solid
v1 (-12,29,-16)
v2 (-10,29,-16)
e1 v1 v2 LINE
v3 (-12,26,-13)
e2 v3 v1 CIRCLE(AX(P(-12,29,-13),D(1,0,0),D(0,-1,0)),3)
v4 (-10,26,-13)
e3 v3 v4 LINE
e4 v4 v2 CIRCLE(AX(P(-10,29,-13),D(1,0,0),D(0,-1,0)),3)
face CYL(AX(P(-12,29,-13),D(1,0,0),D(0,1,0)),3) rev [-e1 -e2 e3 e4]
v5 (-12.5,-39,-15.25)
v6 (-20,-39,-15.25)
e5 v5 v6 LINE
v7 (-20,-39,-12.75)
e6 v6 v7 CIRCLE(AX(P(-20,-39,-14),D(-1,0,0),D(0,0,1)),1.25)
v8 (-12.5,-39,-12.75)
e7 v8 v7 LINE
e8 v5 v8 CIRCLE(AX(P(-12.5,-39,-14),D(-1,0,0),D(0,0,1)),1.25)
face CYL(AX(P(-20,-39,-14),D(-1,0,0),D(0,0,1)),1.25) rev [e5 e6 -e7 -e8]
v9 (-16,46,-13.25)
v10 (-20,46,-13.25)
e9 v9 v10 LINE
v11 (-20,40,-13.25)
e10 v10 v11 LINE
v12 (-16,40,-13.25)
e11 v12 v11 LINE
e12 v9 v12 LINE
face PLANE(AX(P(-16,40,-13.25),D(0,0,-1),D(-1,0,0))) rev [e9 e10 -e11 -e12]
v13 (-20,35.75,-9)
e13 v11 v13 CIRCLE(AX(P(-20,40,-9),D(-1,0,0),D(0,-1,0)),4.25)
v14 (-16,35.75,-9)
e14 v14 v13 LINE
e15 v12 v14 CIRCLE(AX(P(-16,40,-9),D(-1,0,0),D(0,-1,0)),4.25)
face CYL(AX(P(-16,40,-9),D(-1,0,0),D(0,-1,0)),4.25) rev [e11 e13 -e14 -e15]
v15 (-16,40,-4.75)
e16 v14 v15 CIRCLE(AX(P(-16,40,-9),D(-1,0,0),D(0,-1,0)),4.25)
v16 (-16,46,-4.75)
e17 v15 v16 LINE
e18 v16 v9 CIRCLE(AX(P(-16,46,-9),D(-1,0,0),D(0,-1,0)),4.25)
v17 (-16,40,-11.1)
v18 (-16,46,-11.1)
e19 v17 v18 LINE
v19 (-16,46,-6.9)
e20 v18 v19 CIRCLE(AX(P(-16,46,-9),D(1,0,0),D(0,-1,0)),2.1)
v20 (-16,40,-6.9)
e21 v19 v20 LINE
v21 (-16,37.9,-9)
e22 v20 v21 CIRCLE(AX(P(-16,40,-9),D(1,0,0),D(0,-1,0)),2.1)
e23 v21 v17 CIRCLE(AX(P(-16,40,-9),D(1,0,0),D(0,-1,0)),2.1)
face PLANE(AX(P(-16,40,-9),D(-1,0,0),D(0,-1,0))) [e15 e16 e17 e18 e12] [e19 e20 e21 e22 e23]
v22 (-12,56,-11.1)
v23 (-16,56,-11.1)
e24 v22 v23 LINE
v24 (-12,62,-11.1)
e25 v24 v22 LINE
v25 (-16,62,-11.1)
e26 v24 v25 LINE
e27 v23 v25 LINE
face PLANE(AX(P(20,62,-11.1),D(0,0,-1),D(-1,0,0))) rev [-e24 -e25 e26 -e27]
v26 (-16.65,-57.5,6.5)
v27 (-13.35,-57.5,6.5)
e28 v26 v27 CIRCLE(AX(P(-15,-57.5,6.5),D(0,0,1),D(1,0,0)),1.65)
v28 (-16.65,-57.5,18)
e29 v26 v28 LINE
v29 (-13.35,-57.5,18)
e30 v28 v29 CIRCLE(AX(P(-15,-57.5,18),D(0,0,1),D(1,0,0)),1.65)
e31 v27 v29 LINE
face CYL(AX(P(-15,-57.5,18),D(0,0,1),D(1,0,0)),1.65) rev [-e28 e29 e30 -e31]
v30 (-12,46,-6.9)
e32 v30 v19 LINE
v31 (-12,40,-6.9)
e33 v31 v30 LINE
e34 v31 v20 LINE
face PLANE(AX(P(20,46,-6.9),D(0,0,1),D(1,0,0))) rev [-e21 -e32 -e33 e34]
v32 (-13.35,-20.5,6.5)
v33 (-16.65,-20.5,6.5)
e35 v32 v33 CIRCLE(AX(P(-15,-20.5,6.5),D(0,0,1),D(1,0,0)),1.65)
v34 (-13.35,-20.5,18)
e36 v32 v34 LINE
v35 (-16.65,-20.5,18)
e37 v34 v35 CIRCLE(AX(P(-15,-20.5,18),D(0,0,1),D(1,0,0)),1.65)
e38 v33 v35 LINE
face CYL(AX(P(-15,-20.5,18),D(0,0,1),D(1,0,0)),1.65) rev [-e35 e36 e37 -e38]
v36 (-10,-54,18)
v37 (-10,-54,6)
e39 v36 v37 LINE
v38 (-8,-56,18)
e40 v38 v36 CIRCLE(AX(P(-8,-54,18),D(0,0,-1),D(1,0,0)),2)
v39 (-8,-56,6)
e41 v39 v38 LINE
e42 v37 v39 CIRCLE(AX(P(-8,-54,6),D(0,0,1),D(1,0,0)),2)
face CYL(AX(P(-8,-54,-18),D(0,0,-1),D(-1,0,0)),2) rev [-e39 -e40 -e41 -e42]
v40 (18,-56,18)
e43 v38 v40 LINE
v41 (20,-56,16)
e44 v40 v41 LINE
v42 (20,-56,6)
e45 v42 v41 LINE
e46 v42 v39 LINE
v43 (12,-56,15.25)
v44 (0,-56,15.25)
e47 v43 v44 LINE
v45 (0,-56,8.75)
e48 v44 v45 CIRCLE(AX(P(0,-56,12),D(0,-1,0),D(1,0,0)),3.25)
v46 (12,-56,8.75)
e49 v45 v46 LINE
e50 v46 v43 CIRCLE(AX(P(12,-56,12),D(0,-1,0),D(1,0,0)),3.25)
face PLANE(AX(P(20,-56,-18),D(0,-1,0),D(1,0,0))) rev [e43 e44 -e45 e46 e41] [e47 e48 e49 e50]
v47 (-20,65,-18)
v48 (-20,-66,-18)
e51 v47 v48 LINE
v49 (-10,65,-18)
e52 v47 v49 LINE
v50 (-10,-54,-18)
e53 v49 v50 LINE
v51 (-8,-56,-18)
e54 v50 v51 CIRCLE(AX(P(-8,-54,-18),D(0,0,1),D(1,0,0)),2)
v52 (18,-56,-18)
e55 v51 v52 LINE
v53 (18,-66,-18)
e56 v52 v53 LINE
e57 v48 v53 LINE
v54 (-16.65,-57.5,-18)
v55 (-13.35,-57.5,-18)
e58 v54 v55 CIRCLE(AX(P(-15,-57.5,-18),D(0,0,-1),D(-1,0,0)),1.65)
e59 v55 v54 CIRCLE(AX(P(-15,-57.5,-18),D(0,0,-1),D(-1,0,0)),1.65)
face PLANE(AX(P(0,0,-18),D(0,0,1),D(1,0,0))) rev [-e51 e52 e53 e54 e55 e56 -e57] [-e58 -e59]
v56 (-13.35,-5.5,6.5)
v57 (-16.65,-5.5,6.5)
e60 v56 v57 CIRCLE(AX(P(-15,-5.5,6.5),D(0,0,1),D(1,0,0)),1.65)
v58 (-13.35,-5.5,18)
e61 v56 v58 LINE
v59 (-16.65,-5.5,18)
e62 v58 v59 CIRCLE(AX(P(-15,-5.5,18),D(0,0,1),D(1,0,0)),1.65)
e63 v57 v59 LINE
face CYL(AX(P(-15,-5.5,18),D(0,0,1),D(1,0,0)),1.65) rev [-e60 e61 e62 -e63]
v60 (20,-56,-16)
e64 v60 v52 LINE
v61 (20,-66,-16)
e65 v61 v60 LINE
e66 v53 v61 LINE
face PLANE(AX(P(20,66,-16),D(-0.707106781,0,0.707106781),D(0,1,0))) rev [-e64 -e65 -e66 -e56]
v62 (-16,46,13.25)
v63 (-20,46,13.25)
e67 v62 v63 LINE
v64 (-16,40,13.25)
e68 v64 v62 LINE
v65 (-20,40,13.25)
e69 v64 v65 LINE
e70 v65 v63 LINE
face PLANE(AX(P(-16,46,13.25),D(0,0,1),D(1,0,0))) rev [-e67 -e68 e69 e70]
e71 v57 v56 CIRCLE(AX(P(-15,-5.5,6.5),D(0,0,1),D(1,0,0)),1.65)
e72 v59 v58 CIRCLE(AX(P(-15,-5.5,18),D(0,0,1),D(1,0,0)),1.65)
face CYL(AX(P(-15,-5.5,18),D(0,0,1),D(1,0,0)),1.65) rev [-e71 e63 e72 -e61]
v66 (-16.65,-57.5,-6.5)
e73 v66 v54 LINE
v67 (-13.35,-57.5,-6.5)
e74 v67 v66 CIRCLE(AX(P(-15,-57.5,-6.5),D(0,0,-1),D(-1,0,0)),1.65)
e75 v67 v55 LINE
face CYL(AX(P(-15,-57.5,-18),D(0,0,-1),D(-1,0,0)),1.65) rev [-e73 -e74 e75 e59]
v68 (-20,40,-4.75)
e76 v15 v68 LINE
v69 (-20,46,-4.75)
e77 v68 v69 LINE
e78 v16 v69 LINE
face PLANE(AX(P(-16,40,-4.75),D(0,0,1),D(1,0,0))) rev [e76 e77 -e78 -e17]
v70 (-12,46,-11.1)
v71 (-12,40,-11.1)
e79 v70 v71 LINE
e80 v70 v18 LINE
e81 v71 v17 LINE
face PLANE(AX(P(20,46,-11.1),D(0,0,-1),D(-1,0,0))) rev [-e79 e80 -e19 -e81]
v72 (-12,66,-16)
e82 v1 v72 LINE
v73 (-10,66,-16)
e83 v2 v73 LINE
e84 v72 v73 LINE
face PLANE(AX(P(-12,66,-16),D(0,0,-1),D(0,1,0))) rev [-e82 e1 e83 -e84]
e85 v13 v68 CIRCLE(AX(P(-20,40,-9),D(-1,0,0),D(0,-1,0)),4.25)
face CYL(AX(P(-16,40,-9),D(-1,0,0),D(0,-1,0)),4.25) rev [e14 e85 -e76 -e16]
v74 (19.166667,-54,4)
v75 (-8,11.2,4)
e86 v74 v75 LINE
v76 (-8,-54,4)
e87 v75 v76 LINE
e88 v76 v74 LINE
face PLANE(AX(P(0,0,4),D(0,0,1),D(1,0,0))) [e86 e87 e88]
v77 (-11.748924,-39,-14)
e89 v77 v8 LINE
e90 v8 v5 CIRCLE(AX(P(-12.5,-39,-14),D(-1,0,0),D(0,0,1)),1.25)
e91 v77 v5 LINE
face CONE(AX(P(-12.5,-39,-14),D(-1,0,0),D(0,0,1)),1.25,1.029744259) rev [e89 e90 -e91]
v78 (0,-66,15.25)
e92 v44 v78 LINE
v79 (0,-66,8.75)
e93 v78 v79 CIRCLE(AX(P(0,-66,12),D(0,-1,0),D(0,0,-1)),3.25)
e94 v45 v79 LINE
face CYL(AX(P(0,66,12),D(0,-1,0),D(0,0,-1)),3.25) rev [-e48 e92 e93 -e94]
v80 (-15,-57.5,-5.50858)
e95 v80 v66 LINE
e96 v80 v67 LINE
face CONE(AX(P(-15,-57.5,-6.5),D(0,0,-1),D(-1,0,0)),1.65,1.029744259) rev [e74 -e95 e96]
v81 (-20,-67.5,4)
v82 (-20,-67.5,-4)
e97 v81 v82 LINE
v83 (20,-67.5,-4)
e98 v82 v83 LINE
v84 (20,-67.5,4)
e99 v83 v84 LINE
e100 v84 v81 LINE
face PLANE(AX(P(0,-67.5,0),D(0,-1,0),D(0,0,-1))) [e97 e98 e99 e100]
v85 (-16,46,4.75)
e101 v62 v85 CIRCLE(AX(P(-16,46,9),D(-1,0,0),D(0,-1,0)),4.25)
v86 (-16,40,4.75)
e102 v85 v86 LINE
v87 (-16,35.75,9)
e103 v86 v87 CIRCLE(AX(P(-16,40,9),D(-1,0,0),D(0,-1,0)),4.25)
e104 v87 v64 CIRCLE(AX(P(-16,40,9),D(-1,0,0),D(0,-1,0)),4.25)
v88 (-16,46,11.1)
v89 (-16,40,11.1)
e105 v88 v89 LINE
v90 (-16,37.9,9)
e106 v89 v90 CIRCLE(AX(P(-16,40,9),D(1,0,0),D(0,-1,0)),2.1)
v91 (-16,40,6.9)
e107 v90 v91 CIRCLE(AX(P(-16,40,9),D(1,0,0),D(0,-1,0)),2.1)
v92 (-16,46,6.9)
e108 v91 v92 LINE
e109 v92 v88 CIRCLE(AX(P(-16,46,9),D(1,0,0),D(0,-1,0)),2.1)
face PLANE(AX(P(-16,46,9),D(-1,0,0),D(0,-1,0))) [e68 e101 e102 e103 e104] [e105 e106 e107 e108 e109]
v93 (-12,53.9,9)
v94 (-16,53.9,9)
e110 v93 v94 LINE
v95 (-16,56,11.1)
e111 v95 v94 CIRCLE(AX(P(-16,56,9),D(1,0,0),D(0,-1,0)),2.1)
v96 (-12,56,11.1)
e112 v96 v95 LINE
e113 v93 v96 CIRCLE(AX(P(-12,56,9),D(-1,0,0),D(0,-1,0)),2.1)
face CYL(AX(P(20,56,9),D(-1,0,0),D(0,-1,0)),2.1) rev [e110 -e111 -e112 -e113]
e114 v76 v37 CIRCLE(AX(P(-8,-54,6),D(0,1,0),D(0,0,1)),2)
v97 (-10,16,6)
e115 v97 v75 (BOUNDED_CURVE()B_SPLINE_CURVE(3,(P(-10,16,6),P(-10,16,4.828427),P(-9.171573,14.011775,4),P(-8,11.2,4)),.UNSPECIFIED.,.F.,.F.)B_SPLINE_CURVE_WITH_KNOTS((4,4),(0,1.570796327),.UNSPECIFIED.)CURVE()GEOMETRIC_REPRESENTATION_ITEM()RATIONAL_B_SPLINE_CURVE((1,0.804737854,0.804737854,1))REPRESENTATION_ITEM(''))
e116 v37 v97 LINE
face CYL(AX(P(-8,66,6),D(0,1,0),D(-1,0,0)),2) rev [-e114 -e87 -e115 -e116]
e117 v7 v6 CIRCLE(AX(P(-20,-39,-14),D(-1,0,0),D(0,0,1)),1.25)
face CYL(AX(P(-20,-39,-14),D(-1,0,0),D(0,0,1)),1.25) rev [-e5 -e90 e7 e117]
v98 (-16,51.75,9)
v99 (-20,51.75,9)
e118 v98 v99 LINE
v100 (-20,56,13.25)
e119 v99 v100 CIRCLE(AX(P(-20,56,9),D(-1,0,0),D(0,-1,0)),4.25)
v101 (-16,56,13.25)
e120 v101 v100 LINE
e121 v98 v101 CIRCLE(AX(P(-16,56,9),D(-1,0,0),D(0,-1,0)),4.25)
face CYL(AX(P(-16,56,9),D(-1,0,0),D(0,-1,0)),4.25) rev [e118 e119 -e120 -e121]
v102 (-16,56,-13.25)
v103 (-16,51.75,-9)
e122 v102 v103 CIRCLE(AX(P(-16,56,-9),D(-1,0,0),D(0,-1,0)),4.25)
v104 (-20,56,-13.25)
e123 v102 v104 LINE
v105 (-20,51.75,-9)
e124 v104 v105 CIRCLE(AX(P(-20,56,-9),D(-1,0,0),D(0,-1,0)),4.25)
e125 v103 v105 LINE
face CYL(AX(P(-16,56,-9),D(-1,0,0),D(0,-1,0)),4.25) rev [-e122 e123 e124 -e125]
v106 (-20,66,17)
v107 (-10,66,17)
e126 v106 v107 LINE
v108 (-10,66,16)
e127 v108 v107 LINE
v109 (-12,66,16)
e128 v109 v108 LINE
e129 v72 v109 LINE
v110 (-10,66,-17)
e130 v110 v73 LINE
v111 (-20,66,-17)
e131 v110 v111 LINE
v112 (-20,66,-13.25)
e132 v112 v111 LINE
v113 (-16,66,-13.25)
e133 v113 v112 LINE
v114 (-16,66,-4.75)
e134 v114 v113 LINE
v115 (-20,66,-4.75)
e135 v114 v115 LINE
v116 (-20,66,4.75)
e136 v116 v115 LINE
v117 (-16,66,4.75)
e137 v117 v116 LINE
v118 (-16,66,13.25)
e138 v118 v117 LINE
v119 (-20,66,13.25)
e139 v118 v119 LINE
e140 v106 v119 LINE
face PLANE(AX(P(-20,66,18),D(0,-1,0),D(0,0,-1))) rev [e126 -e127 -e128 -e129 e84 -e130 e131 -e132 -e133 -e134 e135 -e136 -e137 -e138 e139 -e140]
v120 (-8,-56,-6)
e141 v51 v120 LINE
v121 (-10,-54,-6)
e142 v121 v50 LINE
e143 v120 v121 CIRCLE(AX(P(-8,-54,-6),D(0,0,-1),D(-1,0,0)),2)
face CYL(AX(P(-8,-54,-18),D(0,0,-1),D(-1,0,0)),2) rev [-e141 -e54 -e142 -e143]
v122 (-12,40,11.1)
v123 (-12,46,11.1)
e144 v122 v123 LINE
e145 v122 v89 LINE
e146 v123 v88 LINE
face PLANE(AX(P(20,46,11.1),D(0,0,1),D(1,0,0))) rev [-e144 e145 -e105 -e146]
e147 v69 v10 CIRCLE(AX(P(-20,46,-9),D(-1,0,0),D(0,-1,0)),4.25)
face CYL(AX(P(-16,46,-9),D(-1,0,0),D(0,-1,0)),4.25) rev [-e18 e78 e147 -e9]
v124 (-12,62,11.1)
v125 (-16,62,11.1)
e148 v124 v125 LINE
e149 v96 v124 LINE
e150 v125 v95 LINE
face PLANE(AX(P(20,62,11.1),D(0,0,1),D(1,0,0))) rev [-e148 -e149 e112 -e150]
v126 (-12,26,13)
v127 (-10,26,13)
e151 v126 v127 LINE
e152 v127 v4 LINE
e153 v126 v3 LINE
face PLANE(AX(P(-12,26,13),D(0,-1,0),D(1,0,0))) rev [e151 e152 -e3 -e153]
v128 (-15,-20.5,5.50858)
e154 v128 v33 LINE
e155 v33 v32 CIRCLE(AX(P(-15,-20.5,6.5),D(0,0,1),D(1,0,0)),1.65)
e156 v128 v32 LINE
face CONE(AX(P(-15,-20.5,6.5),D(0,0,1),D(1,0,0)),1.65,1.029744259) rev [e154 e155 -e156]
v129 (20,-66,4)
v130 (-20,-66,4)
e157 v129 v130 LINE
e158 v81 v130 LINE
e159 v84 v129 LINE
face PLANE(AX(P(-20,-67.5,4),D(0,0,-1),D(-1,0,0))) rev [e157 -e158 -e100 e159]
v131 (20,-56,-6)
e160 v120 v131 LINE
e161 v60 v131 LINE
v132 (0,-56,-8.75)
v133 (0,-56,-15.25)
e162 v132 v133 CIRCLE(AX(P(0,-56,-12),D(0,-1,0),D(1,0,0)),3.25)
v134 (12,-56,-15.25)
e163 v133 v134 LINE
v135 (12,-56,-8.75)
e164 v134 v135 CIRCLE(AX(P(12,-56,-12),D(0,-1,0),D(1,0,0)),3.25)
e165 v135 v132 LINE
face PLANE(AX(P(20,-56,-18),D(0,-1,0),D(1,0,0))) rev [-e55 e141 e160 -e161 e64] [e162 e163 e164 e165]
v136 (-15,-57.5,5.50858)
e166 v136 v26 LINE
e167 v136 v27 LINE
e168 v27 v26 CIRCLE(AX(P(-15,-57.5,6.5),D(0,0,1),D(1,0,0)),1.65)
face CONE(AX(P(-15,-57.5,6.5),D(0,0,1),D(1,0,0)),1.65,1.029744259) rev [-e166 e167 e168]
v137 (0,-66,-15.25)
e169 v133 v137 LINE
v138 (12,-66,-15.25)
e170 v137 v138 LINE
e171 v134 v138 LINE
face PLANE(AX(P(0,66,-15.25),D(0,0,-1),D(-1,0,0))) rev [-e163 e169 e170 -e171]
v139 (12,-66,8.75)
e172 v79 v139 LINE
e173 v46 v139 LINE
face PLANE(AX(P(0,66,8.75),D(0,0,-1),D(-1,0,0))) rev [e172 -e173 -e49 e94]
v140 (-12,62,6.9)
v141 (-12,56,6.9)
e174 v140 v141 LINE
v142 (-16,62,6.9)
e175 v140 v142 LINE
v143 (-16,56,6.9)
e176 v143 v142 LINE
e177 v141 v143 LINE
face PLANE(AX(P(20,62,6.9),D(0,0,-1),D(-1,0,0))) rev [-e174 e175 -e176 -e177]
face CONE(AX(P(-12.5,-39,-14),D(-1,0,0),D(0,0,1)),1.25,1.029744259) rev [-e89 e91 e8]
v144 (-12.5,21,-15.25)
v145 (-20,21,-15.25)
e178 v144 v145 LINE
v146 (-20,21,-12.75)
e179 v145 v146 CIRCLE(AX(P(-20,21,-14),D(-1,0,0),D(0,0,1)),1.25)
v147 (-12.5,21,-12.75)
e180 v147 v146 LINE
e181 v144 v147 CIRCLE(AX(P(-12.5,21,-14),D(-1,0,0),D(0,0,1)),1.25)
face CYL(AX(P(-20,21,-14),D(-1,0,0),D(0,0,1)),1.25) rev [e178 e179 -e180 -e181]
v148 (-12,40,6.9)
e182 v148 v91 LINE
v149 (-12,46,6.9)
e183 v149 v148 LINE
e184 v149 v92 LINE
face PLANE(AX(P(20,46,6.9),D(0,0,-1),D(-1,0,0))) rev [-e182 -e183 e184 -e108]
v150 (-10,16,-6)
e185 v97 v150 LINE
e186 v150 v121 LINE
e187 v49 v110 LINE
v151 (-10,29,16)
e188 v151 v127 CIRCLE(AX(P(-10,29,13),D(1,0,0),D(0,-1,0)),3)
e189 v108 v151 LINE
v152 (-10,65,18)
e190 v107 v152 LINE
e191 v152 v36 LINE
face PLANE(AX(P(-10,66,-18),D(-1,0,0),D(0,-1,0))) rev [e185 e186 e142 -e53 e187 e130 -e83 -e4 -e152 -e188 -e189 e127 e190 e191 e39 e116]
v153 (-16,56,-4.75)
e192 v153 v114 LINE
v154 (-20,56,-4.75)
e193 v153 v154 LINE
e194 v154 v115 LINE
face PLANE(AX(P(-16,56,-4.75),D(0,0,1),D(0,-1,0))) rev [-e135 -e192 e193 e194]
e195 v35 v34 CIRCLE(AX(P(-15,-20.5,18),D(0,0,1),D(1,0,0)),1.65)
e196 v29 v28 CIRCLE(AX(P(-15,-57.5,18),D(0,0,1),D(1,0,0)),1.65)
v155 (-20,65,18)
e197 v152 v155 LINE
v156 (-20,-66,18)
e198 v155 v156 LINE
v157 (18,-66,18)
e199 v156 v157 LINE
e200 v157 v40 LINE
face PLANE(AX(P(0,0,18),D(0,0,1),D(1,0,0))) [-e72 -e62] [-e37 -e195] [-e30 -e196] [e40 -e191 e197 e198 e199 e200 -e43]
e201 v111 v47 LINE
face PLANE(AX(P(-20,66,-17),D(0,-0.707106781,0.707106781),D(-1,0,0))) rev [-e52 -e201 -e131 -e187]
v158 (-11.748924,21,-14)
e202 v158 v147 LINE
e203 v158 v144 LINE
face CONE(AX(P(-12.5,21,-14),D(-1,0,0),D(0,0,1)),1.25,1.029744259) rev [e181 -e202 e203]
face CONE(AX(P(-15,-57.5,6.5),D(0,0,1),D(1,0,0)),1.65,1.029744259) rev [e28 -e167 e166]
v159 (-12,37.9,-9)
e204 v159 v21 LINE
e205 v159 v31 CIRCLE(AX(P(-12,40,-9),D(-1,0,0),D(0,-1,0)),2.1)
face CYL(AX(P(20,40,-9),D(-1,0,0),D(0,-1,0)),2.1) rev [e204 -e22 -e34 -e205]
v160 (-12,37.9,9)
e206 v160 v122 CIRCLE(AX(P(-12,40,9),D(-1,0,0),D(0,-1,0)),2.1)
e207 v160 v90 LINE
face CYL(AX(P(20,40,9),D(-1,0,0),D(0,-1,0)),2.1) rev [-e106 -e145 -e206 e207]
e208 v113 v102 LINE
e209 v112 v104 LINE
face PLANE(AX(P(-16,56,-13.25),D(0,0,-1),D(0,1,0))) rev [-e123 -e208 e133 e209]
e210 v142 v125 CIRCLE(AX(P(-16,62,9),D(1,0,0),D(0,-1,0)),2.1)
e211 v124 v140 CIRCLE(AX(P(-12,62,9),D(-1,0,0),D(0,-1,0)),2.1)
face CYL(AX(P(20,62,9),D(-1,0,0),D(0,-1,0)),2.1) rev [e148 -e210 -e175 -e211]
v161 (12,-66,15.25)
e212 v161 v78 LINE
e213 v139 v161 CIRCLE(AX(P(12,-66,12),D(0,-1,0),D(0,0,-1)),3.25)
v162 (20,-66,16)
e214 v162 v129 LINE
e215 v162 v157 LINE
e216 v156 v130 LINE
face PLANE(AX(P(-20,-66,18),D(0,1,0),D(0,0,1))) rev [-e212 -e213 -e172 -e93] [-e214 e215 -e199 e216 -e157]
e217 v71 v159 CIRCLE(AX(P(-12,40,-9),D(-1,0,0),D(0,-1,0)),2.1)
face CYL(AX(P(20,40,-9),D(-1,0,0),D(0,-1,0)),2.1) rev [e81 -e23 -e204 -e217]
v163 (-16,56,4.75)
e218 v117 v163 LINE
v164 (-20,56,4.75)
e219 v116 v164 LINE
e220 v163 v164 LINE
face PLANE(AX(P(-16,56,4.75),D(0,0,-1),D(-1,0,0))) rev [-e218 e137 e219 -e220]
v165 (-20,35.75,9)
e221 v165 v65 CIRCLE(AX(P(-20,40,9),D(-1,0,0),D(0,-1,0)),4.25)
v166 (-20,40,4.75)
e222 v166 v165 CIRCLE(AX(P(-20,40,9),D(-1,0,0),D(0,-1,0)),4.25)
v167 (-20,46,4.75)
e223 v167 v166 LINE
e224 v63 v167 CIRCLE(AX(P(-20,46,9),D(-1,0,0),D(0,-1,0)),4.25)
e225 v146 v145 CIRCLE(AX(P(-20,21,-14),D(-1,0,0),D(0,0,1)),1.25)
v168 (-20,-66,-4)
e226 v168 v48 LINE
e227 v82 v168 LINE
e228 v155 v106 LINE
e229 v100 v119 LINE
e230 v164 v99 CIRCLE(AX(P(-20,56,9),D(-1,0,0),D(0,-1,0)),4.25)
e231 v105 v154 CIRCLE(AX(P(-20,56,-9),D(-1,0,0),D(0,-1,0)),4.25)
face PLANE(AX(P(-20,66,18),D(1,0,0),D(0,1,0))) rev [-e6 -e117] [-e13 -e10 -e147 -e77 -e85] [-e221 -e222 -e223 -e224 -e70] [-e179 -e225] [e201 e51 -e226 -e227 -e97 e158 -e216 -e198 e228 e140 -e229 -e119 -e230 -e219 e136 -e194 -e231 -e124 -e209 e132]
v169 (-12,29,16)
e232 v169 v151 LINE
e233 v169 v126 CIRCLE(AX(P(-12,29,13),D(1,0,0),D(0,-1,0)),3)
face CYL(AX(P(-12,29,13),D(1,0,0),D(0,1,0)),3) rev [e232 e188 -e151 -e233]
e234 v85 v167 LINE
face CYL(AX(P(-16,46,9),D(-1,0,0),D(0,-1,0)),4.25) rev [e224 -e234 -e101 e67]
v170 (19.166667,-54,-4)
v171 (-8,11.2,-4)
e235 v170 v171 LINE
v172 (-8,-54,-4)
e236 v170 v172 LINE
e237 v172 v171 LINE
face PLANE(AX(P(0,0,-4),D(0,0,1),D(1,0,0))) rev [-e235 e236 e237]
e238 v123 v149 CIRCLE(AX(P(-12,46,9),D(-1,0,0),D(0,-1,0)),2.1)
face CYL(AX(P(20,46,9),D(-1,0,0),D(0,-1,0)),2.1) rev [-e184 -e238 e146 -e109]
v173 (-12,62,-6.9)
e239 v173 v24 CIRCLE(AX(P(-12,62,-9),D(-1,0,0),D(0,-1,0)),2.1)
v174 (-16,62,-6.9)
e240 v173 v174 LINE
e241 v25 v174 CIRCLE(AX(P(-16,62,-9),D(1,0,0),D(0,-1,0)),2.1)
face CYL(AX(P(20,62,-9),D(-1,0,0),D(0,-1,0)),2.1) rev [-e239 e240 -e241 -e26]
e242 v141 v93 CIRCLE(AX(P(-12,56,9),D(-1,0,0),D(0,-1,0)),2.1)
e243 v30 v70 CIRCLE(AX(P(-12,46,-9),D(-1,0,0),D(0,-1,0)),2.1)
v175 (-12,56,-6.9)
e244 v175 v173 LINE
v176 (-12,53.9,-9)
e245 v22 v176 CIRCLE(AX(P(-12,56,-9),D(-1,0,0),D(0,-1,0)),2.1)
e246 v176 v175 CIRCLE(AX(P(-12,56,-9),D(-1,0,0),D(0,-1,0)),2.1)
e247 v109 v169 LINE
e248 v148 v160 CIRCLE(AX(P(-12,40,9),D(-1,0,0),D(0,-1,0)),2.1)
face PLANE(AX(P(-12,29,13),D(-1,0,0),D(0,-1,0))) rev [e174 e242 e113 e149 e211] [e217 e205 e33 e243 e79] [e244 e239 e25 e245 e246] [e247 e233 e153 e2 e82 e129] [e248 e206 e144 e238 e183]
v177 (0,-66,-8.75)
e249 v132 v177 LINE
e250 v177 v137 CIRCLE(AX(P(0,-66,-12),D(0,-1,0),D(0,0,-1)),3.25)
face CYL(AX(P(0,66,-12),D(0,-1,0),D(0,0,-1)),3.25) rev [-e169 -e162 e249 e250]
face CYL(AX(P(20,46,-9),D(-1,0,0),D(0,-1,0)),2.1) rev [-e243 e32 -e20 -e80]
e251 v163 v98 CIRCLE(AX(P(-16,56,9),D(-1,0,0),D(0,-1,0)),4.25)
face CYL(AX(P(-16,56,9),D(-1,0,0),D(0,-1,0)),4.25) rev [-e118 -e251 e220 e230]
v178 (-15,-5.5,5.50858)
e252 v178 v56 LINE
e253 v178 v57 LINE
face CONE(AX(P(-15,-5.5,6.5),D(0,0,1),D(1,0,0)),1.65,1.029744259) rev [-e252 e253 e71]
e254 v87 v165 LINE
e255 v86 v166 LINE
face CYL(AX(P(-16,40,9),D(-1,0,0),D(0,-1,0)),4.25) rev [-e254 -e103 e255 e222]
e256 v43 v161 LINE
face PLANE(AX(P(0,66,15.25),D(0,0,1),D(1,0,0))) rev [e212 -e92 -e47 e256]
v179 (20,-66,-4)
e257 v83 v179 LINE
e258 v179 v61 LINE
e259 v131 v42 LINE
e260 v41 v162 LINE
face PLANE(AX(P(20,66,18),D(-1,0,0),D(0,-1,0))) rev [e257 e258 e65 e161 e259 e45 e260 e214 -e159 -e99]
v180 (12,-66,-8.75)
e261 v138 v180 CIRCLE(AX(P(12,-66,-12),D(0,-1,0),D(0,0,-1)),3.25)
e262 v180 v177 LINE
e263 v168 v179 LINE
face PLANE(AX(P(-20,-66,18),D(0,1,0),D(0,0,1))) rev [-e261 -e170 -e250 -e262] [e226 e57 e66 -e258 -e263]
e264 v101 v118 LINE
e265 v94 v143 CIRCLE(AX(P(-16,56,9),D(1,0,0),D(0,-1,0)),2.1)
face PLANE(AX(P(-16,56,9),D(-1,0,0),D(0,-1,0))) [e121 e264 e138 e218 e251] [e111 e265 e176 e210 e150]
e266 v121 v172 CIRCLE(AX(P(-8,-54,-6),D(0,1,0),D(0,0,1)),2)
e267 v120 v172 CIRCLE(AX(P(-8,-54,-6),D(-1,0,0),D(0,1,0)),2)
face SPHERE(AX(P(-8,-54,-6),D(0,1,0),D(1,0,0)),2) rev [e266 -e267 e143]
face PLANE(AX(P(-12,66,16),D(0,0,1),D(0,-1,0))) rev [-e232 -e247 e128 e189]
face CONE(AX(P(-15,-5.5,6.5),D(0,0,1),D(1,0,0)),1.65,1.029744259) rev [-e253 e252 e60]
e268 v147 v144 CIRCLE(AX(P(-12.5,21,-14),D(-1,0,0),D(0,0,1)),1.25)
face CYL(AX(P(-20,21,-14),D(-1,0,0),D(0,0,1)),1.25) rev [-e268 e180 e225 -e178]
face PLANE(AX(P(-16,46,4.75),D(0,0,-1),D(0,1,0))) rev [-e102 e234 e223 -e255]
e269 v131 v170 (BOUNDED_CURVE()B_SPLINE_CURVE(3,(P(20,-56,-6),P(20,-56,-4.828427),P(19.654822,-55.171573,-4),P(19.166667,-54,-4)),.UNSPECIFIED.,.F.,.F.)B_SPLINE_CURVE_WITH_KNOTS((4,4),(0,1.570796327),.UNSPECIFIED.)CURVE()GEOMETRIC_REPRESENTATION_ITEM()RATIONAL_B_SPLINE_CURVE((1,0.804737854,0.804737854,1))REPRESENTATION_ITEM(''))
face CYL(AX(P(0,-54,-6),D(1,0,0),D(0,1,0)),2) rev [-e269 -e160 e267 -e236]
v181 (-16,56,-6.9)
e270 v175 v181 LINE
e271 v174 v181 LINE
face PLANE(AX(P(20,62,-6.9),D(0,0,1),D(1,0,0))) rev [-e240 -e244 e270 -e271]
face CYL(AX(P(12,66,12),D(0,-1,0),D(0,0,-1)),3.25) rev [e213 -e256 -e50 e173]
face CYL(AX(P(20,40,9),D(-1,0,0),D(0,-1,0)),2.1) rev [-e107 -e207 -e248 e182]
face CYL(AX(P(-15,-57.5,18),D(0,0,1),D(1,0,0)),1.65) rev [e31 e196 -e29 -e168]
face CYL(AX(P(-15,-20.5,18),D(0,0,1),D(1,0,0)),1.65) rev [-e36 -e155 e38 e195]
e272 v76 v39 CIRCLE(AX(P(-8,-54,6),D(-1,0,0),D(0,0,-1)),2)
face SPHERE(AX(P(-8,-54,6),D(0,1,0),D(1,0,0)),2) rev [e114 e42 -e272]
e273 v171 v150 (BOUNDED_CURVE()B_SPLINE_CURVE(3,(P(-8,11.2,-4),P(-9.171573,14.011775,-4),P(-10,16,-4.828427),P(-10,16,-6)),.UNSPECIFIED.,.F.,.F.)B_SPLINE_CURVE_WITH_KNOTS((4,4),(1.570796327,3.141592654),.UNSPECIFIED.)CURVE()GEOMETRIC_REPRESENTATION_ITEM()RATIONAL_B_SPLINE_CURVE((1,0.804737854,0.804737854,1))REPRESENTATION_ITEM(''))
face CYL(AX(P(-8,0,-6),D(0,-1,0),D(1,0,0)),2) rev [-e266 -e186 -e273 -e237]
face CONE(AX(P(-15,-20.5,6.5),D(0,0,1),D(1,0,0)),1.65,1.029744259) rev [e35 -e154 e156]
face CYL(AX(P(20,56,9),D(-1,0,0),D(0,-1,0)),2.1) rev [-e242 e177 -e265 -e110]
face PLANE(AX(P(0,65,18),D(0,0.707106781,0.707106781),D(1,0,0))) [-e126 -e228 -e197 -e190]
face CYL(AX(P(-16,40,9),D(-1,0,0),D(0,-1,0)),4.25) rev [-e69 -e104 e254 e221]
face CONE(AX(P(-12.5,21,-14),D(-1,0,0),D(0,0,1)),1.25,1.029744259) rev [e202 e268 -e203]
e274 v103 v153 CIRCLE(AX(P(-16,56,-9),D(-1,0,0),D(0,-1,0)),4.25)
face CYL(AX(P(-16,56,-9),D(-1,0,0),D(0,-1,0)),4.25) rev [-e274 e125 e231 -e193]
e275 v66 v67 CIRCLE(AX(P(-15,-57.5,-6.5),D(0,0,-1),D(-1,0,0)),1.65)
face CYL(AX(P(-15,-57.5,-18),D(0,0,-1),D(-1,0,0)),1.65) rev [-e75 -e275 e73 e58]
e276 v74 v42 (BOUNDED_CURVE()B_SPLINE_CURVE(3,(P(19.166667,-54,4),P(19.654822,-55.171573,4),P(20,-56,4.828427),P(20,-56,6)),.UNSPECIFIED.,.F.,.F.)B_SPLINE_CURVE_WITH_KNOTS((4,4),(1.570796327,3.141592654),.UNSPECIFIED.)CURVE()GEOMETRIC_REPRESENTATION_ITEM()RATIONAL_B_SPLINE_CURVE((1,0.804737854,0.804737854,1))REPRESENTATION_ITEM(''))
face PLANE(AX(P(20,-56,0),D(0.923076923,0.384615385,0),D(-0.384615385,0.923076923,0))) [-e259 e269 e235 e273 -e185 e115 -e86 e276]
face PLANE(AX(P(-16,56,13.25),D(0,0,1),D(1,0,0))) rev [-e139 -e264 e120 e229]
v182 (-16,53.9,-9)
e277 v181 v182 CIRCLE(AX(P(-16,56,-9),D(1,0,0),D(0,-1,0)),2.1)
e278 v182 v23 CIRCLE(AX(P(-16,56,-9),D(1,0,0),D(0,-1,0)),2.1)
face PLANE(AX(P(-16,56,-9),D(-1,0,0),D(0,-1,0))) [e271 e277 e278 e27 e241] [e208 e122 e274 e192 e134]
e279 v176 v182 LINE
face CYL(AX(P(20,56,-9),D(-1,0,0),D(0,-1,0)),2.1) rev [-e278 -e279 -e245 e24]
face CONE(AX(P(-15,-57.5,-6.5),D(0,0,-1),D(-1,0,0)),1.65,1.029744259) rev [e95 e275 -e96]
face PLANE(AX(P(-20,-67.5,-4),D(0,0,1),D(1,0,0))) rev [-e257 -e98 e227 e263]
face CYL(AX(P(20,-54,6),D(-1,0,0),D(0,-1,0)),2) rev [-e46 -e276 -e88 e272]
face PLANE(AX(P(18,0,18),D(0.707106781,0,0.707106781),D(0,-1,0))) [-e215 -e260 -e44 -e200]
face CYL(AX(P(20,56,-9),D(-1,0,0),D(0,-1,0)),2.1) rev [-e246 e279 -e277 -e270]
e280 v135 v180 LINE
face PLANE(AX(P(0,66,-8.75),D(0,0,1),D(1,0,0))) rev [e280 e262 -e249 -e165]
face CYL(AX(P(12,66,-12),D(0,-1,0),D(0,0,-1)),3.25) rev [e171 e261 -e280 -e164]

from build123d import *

# Parameters (mm, degrees)
SKETCH1_W             = 40
SKETCH1_H             = 132
BOSS_EXTRUDE1_DEPTH   = 18
SKETCH2_W             = 30
SKETCH2_H             = 122
CUT_EXTRUDE1_DEPTH    = 78.794601355
RIB2_REACH            = 73.274
SKETCH3_WALL_W        = 222.54823745
SKETCH3_WALL_H        = 8
FILLET1_R             = 2
CUT_EXTRUDE2_DEPTH    = 2
CUT_EXTRUDE3_DEPTH    = 80.246451025
CUT_EXTRUDE4_DEPTH    = 4
SKETCH9_W             = 40
SKETCH9_H             = 8
BOSS_EXTRUDE2_DEPTH   = 1.5
CUT_EXTRUDE5_DEPTH    = 135.714512952
CHAMFER1_SIZE         = 1
CHAMFER2_SIZE         = 2
M3_TAPPED_HOLE2_D     = 2.5
M3_TAPPED_HOLE2_DEPTH = 7.5
M3_TAPPED_HOLE2_TIP   = 0.751075774
M4_TAPPED_HOLE2_D     = 3.3
M4_TAPPED_HOLE2_DEPTH = 11.5
M4_TAPPED_HOLE2_TIP   = 0.991420021


with BuildPart() as part:
    # Sketch1 → Boss-Extrude1 (new, symmetric)
    with BuildSketch(Plane.XY):
        Rectangle(SKETCH1_W, SKETCH1_H)
    extrude(amount=BOSS_EXTRUDE1_DEPTH, both=True)

    # Sketch2 → Cut-Extrude1 (cut, through all)
    with BuildSketch(Plane.XY.offset(18)):
        with Locations((5, 5)):
            Rectangle(SKETCH2_W, SKETCH2_H)
    extrude(amount=-CUT_EXTRUDE1_DEPTH, mode=Mode.SUBTRACT)

    # Sketch3 wall → Rib2 (add, up to next)
    with BuildSketch(Plane(origin=(5, -20, 0), x_dir=(-0.384615384615, 0.923076923077, 0), z_dir=(-0.923076923077, -0.384615384615, 0)), mode=Mode.PRIVATE) as rib2_sk1:
        Rectangle(SKETCH3_WALL_W, SKETCH3_WALL_H)
    rib2_tool1 = extrude(rib2_sk1.sketch, amount=RIB2_REACH, mode=Mode.PRIVATE) - part.part
    add(rib2_tool1.solids().sort_by_distance((5, -20, 0))[0])

    # Fillet1
    fillet1_edges = [part.edges().sort_by_distance(p)[0] for p in [
        (-10, -56, -11),
        (-10, -56, 11),
        (-10, -20, -4),
        (-10, -20, 4),
        (5, -56, -4),
        (5, -56, 4),
    ]]
    fillet(fillet1_edges, radius=FILLET1_R)

    # Sketch4 → Cut-Extrude2 (cut)
    with BuildSketch(Plane(origin=(-10, 0, 0), x_dir=(0, 0, -1), z_dir=(1, 0, 0))):
        with BuildLine():
            Line((-16, 66), (16, 66))
            Line((16, 66), (16, 29))
            ThreePointArc((16, 29), (15.121320344, 26.878679656), (13, 26))
            Line((13, 26), (-13, 26))
            ThreePointArc((-13, 26), (-15.121320344, 26.878679656), (-16, 29))
            Line((-16, 29), (-16, 66))
        make_face()
    extrude(amount=-CUT_EXTRUDE2_DEPTH, mode=Mode.SUBTRACT)

    # Sketch5 → Cut-Extrude3 (cut, through all)
    with BuildSketch(Plane.ZY.offset(20)):
        with BuildLine():
            Line((-6.9, 62), (-6.9, 56))
            ThreePointArc((-6.9, 56), (-9, 53.9), (-11.1, 56))
            Line((-11.1, 56), (-11.1, 62))
            ThreePointArc((-11.1, 62), (-9, 64.1), (-6.9, 62))
        make_face()
        with BuildLine():
            Line((11.1, 62), (11.1, 56))
            ThreePointArc((11.1, 56), (9, 53.9), (6.9, 56))
            Line((6.9, 56), (6.9, 62))
            ThreePointArc((6.9, 62), (9, 64.1), (11.1, 62))
        make_face()
        with BuildLine():
            Line((11.1, 46), (11.1, 40))
            ThreePointArc((11.1, 40), (9, 37.9), (6.9, 40))
            Line((6.9, 40), (6.9, 46))
            ThreePointArc((6.9, 46), (9, 48.1), (11.1, 46))
        make_face()
        with BuildLine():
            Line((-6.9, 46), (-6.9, 40))
            ThreePointArc((-6.9, 40), (-9, 37.9), (-11.1, 40))
            Line((-11.1, 40), (-11.1, 46))
            ThreePointArc((-11.1, 46), (-9, 48.1), (-6.9, 46))
        make_face()
    extrude(amount=-CUT_EXTRUDE3_DEPTH, mode=Mode.SUBTRACT)

    # Sketch8 → Cut-Extrude4 (cut)
    with BuildSketch(Plane.ZY.offset(20)):
        with BuildLine():
            Line((-13.25, 56), (-13.25, 66))
            ThreePointArc((-13.25, 66), (-9, 70.25), (-4.75, 66))
            Line((-4.75, 66), (-4.75, 56))
            ThreePointArc((-4.75, 56), (-9, 51.75), (-13.25, 56))
        make_face()
        with BuildLine():
            Line((4.75, 56), (4.75, 66))
            ThreePointArc((4.75, 66), (9, 70.25), (13.25, 66))
            Line((13.25, 66), (13.25, 56))
            ThreePointArc((13.25, 56), (9, 51.75), (4.75, 56))
        make_face()
        with BuildLine():
            Line((-13.25, 40), (-13.25, 46))
            ThreePointArc((-13.25, 46), (-9, 50.25), (-4.75, 46))
            Line((-4.75, 46), (-4.75, 40))
            ThreePointArc((-4.75, 40), (-9, 35.75), (-13.25, 40))
        make_face()
        with BuildLine():
            Line((13.25, 46), (13.25, 40))
            ThreePointArc((13.25, 40), (9, 35.75), (4.75, 40))
            Line((4.75, 40), (4.75, 46))
            ThreePointArc((4.75, 46), (9, 50.25), (13.25, 46))
        make_face()
    extrude(amount=-CUT_EXTRUDE4_DEPTH, mode=Mode.SUBTRACT)

    # Sketch9 → Boss-Extrude2 (add)
    with BuildSketch(Plane.XZ.offset(66)):
        Rectangle(SKETCH9_W, SKETCH9_H)
    extrude(amount=BOSS_EXTRUDE2_DEPTH)

    # Sketch10 → Cut-Extrude5 (cut, through all)
    with BuildSketch(Plane.XZ.offset(66)):
        with BuildLine():
            Line((0, 15.25), (12, 15.25))
            ThreePointArc((12, 15.25), (15.25, 12), (12, 8.75))
            Line((12, 8.75), (0, 8.75))
            ThreePointArc((0, 8.75), (-3.25, 12), (0, 15.25))
        make_face()
        with BuildLine():
            Line((0, -8.75), (12, -8.75))
            ThreePointArc((12, -8.75), (15.25, -12), (12, -15.25))
            Line((12, -15.25), (0, -15.25))
            ThreePointArc((0, -15.25), (-3.25, -12), (0, -8.75))
        make_face()
    extrude(amount=-CUT_EXTRUDE5_DEPTH, mode=Mode.SUBTRACT)

    # Chamfer1
    chamfer1_edges = [part.edges().sort_by_distance(p)[0] for p in [
        (-15, 66, -18),
        (-15, 66, 18),
    ]]
    chamfer(chamfer1_edges, length=CHAMFER1_SIZE)

    # Chamfer2
    chamfer2_edges = [part.edges().sort_by_distance(p)[0] for p in [
        (20, -61, -18),
        (20, -61, 18),
    ]]
    chamfer(chamfer2_edges, length=CHAMFER2_SIZE)

    # M3 Tapped Hole2
    with Locations(Plane.ZY.offset(20)):
        with Locations((-14, 21), (-14, -39)):
            Hole(M3_TAPPED_HOLE2_D / 2, depth=M3_TAPPED_HOLE2_DEPTH)
            with Locations((0, 0, -(M3_TAPPED_HOLE2_DEPTH + M3_TAPPED_HOLE2_TIP / 2))):  # 118° drill point
                Cone(0, M3_TAPPED_HOLE2_D / 2, M3_TAPPED_HOLE2_TIP, mode=Mode.SUBTRACT)

    # M4 Tapped Hole2
    with Locations(Plane.XY.offset(18)):
        with Locations((-15, -5.5), (-15, -20.5)):
            Hole(M4_TAPPED_HOLE2_D / 2, depth=M4_TAPPED_HOLE2_DEPTH)
            with Locations((0, 0, -(M4_TAPPED_HOLE2_DEPTH + M4_TAPPED_HOLE2_TIP / 2))):  # 118° drill point
                Cone(0, M4_TAPPED_HOLE2_D / 2, M4_TAPPED_HOLE2_TIP, mode=Mode.SUBTRACT)

    # Sketch19 → M4 Tapped Hole3 (revolve, cut)
    with BuildSketch(Plane(origin=(-15, -57.5, 18), x_dir=(0, -1, 0), z_dir=(1, 0, 0))):
        Polygon((0, 0), (0, 12.491420021), (1.65, 11.5), (1.65, 0), align=None)
    m4_tapped_hole3 = revolve(axis=Axis((-15, -57.5, 24.35), (0, 0, -1)), mode=Mode.SUBTRACT)

    # Mirror1: M4 Tapped Hole3 across plane
    add(m4_tapped_hole3.mirror(Plane.XY), mode=Mode.SUBTRACT)


solid = part.part
